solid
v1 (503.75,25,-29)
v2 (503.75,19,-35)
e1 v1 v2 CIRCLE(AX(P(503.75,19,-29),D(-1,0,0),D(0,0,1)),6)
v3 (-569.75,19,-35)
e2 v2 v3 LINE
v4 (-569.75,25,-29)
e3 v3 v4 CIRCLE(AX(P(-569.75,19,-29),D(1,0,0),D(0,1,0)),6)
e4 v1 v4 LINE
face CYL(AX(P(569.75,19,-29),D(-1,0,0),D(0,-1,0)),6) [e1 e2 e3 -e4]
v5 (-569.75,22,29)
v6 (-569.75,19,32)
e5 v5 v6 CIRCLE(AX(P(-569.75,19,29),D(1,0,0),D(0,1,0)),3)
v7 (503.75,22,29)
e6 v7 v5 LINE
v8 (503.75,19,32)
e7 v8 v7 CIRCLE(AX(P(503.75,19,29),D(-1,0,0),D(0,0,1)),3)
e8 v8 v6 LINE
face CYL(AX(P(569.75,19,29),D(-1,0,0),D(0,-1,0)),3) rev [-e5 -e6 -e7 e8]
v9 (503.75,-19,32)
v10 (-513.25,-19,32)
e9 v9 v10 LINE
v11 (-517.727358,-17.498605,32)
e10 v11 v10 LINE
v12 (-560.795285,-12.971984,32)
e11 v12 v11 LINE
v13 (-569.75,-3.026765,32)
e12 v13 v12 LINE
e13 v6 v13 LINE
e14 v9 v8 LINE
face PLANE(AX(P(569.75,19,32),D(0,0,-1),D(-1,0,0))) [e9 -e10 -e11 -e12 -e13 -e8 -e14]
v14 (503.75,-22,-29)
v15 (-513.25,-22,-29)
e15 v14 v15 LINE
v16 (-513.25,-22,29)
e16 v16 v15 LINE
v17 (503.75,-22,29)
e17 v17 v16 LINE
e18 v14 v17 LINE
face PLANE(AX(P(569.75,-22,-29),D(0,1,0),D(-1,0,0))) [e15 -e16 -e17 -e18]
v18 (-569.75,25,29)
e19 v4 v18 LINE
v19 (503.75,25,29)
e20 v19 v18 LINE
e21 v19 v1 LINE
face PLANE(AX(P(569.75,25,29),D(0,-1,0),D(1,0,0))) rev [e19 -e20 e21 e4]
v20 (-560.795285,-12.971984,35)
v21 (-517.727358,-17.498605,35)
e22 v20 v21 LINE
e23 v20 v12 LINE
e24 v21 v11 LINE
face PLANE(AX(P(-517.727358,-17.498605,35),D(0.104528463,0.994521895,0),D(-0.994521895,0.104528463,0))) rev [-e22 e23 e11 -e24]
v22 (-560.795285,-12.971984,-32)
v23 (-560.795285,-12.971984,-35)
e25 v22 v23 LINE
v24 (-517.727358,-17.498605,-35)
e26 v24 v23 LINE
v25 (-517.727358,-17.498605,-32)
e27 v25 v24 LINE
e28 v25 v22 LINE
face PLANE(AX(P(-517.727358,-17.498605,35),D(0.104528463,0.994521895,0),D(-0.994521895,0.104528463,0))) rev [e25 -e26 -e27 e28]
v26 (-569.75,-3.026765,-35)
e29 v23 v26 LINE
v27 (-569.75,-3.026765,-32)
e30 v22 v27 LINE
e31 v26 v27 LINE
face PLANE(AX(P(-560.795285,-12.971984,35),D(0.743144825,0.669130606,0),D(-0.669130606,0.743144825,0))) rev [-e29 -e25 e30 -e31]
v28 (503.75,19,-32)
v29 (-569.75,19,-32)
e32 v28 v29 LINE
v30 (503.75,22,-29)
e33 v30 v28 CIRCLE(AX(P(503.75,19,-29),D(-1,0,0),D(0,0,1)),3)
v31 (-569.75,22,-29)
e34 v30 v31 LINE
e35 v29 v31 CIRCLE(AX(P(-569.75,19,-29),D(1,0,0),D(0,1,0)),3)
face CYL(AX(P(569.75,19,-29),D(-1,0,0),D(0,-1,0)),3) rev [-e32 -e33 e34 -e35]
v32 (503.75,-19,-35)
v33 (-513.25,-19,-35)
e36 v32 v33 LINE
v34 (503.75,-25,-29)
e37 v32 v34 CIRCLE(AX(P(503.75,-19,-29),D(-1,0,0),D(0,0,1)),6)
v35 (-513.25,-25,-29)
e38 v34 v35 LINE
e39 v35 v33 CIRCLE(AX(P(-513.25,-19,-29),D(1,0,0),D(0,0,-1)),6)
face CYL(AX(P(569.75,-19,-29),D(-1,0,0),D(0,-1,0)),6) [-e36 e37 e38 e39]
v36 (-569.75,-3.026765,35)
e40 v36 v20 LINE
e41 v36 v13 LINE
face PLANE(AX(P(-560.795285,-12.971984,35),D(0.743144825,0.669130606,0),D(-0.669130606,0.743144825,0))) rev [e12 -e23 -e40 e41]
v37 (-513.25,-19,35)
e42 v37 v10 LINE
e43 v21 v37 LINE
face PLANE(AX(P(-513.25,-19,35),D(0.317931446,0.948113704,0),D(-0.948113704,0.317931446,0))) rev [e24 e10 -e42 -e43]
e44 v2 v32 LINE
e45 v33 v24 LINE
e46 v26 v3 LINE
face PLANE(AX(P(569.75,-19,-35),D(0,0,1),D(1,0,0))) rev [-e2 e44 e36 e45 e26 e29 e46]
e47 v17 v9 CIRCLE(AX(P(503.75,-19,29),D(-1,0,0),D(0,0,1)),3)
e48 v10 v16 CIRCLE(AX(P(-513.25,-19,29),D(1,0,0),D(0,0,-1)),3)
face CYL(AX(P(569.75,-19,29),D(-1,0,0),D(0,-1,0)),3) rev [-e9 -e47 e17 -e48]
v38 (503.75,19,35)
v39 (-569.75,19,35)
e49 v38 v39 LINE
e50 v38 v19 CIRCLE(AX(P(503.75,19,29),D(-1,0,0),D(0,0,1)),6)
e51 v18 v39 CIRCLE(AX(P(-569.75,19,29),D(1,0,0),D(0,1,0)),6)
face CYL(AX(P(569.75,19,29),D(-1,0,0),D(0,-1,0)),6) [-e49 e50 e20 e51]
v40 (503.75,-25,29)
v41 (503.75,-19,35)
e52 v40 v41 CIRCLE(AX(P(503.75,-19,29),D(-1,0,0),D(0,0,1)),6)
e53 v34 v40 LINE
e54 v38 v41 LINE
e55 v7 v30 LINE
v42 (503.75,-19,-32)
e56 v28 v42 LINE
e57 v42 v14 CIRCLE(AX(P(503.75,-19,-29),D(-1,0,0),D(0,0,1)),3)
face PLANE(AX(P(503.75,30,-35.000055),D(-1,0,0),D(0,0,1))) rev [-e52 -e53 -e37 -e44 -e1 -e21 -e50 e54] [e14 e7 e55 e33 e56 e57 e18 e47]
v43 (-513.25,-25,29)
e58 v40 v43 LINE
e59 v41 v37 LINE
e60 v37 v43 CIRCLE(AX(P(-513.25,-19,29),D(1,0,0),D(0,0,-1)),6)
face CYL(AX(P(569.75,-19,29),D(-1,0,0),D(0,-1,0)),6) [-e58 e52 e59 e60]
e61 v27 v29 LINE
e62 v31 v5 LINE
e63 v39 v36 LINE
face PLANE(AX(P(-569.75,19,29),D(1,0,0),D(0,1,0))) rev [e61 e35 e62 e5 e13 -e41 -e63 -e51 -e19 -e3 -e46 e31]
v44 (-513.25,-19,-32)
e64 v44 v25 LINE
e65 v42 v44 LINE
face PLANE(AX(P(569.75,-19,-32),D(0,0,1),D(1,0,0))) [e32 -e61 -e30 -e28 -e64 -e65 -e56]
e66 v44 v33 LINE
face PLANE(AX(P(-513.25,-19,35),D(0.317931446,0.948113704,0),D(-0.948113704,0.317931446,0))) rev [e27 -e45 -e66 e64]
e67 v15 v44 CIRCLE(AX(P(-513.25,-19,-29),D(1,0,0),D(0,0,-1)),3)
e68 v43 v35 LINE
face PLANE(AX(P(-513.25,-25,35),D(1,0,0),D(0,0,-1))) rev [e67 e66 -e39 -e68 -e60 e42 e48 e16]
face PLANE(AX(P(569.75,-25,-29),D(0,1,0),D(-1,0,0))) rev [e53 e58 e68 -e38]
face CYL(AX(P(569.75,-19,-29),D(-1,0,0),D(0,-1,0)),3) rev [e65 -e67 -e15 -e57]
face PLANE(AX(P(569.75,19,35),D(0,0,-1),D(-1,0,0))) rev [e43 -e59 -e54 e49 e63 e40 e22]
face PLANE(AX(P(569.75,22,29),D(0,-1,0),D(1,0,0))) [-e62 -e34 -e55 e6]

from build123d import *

# Parameters (mm, degrees)
GB_6728_1986_070_X_50_X_3_1_DEPTH = 1139.5
CUT_EXTRUDE_1_DEPTH               = 575.578160479
CUT_EXTRUDE_1_DEPTH_BACK          = 575.578160479
SKETCH_5_W                        = 71
SKETCH_5_H                        = 60
CUT_EXTRUDE_4_DEPTH               = 575.578160479


with BuildPart() as part:
    # Sketch1 → Gb／6728-1986矩形空心型钢 070 X 50 X 3(1) (new body)
    with BuildSketch(Plane.YZ.offset(-569.75)):
        with BuildLine():
            Line((-19, -35), (19, -35))
            ThreePointArc((19, -35), (23.242640687, -33.242640687), (25, -29))
            Line((25, -29), (25, 29))
            ThreePointArc((25, 29), (23.242640687, 33.242640687), (19, 35))
            Line((19, 35), (-19, 35))
            ThreePointArc((-19, 35), (-23.242640687, 33.242640687), (-25, 29))
            Line((-25, 29), (-25, -29))
            ThreePointArc((-25, -29), (-23.242640687, -33.242640687), (-19, -35))
        make_face()
        with BuildLine():
            Line((-19, -32), (19, -32))
            ThreePointArc((19, -32), (21.121320344, -31.121320344), (22, -29))
            Line((22, -29), (22, 29))
            ThreePointArc((22, 29), (21.121320344, 31.121320344), (19, 32))
            Line((19, 32), (-19, 32))
            ThreePointArc((-19, 32), (-21.121320344, 31.121320344), (-22, 29))
            Line((-22, 29), (-22, -29))
            ThreePointArc((-22, -29), (-21.121320344, -31.121320344), (-19, -32))
        make_face(mode=Mode.SUBTRACT)
    extrude(amount=GB_6728_1986_070_X_50_X_3_1_DEPTH)

    # 草图2 → 切除-拉伸1 (cut, two sides: drawn at the far end of the back side and taken through both)
    with BuildSketch(Plane(origin=(0, 0, -35), x_dir=(-1, 0, 0), z_dir=(0, 0, -1)).offset(-CUT_EXTRUDE_1_DEPTH_BACK)):
        Polygon((513.25, -25), (513.25, -19), (517.727357684, -17.498605391), (560.795284633, -12.971983864), (569.75, -3.026764911), (574.75, -3.026764911), (574.75, -30), (513.25, -30), align=None)
    extrude(amount=CUT_EXTRUDE_1_DEPTH + CUT_EXTRUDE_1_DEPTH_BACK, mode=Mode.SUBTRACT)

    # 草图5 → 切除-拉伸4 (cut, through all)
    with BuildSketch(Plane.XY.offset(35)):
        with Locations((539.25, 0)):
            Rectangle(SKETCH_5_W, SKETCH_5_H)
    extrude(amount=-CUT_EXTRUDE_4_DEPTH, mode=Mode.SUBTRACT)


solid = part.part
